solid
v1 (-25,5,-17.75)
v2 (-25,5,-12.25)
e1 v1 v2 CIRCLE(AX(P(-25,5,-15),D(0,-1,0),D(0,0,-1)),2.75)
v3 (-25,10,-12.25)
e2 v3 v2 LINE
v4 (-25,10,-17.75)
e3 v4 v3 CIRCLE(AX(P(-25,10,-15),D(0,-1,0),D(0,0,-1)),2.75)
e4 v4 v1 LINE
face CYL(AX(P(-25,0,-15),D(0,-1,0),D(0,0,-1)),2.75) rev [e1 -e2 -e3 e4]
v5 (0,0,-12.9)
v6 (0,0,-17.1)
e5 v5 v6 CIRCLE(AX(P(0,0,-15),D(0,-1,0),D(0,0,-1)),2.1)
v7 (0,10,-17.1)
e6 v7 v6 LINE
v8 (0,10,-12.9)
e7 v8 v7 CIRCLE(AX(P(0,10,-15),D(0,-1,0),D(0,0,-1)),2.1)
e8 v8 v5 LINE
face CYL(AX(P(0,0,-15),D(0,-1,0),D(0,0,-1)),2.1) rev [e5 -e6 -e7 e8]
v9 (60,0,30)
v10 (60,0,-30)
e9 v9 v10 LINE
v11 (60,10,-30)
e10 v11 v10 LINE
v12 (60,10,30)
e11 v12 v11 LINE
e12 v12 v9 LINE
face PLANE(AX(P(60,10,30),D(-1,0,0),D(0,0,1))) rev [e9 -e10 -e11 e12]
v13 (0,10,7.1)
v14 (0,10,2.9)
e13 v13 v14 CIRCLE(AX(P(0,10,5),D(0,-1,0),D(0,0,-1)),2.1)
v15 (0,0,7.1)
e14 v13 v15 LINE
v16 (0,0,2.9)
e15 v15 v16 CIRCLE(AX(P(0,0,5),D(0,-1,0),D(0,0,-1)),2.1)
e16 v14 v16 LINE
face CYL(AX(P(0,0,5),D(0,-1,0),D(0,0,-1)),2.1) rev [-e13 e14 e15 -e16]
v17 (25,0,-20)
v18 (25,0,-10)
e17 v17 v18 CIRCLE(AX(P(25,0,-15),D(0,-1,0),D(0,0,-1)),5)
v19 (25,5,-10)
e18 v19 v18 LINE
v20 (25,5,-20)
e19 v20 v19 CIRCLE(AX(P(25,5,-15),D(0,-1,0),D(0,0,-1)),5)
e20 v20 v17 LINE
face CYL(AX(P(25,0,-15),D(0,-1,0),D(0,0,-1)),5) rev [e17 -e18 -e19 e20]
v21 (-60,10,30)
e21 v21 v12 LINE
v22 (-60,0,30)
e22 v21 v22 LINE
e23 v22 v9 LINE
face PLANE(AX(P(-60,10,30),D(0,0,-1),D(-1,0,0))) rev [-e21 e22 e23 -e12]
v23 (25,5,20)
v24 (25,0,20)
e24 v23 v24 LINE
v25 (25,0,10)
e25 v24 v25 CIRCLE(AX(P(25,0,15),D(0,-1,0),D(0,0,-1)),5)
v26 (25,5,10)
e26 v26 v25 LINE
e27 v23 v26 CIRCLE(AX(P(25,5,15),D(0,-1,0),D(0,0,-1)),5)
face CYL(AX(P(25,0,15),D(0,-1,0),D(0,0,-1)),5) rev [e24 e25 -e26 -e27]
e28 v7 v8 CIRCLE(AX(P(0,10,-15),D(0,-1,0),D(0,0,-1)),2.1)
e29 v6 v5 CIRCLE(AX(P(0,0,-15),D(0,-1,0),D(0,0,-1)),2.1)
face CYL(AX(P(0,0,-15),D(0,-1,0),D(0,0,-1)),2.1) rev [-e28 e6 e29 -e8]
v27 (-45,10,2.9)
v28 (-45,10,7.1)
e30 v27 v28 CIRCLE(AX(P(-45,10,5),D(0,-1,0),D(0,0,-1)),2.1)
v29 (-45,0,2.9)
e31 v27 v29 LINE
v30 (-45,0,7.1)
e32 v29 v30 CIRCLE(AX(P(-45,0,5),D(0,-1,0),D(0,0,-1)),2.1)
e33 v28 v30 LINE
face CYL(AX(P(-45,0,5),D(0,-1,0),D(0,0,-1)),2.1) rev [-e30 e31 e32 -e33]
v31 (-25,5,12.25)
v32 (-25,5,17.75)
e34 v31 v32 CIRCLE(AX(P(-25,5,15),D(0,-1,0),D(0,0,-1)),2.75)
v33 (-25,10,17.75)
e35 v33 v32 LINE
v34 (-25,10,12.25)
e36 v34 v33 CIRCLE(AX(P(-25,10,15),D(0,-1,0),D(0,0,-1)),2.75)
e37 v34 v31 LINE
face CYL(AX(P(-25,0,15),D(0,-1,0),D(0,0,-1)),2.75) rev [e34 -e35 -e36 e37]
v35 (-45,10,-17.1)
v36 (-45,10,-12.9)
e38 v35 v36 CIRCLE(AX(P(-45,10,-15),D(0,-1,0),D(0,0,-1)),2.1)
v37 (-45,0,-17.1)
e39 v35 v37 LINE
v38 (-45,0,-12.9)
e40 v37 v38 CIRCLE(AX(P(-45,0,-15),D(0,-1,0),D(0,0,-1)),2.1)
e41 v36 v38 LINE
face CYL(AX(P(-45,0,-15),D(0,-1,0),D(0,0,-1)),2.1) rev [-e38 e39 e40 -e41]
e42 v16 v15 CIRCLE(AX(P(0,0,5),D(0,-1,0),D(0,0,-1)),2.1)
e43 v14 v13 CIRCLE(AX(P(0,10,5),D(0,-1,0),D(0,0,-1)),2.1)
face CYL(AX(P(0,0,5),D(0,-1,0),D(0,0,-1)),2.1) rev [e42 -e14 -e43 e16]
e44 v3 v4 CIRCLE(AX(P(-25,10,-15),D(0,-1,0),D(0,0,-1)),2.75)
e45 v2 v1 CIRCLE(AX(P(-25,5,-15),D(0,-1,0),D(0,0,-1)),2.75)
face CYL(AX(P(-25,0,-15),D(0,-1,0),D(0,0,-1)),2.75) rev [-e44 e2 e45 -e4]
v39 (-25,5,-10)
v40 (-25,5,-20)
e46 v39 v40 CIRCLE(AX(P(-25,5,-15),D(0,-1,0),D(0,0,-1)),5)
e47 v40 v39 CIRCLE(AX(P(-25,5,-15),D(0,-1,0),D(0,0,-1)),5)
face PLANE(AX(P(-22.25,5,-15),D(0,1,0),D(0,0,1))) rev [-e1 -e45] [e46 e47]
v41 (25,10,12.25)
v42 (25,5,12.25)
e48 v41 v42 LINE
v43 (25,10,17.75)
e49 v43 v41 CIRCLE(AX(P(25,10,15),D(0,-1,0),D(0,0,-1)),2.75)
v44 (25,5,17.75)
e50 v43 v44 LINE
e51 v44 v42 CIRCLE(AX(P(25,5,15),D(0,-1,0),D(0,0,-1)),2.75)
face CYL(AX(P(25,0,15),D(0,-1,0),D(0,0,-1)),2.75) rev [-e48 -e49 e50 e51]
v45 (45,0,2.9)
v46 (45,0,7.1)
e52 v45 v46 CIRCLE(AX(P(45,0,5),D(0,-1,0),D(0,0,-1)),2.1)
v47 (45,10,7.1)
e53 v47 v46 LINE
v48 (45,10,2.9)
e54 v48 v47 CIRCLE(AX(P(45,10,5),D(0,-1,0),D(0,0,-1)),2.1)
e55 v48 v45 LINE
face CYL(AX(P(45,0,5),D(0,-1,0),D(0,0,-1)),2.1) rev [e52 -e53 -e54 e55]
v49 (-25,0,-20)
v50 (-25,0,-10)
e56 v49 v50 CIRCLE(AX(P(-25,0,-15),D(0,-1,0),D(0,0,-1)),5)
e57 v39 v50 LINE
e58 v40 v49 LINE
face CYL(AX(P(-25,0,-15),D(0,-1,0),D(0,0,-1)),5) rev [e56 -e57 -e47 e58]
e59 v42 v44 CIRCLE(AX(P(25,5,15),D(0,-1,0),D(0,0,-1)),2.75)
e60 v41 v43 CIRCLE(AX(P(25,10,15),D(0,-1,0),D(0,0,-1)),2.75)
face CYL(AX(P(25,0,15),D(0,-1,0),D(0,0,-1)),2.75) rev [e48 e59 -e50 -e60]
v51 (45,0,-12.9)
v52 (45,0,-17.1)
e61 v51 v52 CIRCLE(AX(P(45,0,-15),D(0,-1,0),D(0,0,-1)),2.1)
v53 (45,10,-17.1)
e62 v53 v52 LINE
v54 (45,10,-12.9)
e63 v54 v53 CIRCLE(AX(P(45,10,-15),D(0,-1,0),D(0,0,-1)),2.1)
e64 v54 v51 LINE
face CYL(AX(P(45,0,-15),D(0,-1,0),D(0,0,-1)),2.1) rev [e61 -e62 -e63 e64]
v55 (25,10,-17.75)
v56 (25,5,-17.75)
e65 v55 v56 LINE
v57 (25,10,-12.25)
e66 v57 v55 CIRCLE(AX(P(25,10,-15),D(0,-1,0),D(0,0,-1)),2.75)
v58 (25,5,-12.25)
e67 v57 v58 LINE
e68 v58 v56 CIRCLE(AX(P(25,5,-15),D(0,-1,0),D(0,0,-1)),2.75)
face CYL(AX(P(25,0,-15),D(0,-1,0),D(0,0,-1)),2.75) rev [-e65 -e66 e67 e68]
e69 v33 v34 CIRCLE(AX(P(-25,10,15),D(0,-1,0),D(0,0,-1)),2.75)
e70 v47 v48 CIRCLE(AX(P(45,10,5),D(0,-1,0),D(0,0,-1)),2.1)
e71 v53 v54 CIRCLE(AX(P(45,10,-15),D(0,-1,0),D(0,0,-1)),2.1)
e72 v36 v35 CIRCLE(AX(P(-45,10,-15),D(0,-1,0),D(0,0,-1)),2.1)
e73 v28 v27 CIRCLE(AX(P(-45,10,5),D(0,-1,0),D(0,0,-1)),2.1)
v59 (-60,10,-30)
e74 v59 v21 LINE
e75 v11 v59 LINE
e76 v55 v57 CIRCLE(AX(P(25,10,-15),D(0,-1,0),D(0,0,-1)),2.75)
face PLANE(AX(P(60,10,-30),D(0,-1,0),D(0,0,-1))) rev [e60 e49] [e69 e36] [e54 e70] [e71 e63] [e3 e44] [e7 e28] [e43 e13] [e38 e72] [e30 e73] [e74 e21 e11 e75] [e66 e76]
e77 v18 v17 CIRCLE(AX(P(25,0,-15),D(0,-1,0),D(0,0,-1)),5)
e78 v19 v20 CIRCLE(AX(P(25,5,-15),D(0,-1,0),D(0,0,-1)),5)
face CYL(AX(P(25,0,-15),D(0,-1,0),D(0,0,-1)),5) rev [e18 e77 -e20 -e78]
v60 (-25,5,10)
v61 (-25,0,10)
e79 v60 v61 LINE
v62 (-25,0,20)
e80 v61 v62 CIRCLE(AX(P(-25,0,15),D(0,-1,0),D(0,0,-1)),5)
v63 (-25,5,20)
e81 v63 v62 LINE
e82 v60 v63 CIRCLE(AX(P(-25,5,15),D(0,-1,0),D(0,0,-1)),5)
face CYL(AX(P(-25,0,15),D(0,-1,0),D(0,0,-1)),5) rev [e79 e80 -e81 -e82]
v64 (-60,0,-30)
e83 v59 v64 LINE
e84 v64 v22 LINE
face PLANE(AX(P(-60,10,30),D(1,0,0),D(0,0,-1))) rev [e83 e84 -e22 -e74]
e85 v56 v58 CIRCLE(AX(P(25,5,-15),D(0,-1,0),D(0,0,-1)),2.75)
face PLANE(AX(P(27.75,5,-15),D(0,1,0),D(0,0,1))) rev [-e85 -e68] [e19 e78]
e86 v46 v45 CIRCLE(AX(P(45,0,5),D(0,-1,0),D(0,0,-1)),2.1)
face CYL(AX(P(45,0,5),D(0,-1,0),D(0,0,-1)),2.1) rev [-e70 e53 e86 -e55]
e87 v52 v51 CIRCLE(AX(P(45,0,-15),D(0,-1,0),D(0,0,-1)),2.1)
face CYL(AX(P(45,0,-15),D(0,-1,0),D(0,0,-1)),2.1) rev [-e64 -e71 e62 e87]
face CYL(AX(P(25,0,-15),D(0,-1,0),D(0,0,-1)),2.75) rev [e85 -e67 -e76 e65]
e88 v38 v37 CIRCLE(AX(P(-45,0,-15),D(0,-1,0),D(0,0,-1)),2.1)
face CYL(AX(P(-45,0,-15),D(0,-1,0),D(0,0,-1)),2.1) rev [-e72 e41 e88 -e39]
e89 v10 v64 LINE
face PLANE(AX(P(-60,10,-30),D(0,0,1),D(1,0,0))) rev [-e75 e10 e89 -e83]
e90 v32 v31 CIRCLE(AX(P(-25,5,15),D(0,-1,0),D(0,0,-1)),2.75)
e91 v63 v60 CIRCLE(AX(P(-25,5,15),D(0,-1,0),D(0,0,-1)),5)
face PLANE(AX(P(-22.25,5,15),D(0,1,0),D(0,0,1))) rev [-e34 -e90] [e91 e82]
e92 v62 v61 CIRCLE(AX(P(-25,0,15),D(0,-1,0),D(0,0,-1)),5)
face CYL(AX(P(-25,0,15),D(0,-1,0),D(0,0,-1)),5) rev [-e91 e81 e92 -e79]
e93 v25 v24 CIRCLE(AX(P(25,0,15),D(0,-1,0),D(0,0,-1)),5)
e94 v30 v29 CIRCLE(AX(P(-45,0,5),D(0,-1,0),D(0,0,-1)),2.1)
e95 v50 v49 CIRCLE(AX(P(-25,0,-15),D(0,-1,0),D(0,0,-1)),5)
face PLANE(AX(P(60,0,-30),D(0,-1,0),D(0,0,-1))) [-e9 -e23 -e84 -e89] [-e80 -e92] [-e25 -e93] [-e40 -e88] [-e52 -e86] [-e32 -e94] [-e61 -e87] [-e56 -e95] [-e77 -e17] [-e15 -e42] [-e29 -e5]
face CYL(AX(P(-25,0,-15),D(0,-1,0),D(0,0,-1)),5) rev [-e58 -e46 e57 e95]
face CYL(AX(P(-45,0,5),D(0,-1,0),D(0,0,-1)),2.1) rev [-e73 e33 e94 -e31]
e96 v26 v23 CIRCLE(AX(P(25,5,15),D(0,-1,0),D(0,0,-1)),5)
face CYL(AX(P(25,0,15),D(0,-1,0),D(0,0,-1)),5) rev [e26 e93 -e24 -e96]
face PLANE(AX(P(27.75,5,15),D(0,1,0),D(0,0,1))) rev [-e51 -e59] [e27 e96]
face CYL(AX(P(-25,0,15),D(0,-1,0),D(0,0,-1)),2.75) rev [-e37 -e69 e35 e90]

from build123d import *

# Parameters (mm, degrees)
SKETCH_1_W                                         = 120
SKETCH_1_H                                         = 60
BOSS_EXTRUDE_1_DEPTH                               = 10
M5_SOCKET_HEAD_CAP_SCREW_COUNTERBORE_1_D           = 5.5
M5_SOCKET_HEAD_CAP_SCREW_COUNTERBORE_1_CBORE_D     = 10
M5_SOCKET_HEAD_CAP_SCREW_COUNTERBORE_1_CBORE_DEPTH = 5
LINEAR_PATTERN_1_COUNT                             = 2
LINEAR_PATTERN_1_PITCH                             = 50
LINEAR_PATTERN_1_COUNT_DIR2                        = 2
LINEAR_PATTERN_1_PITCH_DIR2                        = 30
M5_TAPPED_HOLE_1_D                                 = 4.2
LINEAR_PATTERN_2_COUNT                             = 2
LINEAR_PATTERN_2_PITCH                             = 20
LINEAR_PATTERN_2_COUNT_DIR2                        = 3
LINEAR_PATTERN_2_PITCH_DIR2                        = 45


with BuildPart() as part:
    # Sketch 1 → Boss-Extrude 1 (new body)
    with BuildSketch(Plane(origin=(0, 0, 0), x_dir=(1, 0, 0), z_dir=(0, 1, 0))):
        Rectangle(SKETCH_1_W, SKETCH_1_H)
    extrude(amount=BOSS_EXTRUDE_1_DEPTH)

    # M5 Socket Head Cap Screw Counterbore 1 (through all)
    with Locations(Plane.XZ):
        with Locations((-25, 15)):
            m5_socket_head_cap_screw_counterbore_1 = CounterBoreHole(M5_SOCKET_HEAD_CAP_SCREW_COUNTERBORE_1_D / 2, M5_SOCKET_HEAD_CAP_SCREW_COUNTERBORE_1_CBORE_D / 2, M5_SOCKET_HEAD_CAP_SCREW_COUNTERBORE_1_CBORE_DEPTH)

    # Linear Pattern 1: M5 Socket Head Cap Screw Counterbore 1 2 × 2
    with Locations(*[(i * LINEAR_PATTERN_1_PITCH, 0, -j * LINEAR_PATTERN_1_PITCH_DIR2) for i in range(LINEAR_PATTERN_1_COUNT) for j in range(LINEAR_PATTERN_1_COUNT_DIR2) if (i, j) != (0, 0)]):
        add(m5_socket_head_cap_screw_counterbore_1, mode=Mode.SUBTRACT)

    # M5 Tapped Hole 1 (through all)
    with Locations(Plane.XZ):
        with Locations((-45, 5)):
            m5_tapped_hole_1 = Hole(M5_TAPPED_HOLE_1_D / 2)

    # Linear Pattern 2: M5 Tapped Hole 1 2 × 3
    with Locations(*[(j * LINEAR_PATTERN_2_PITCH_DIR2, 0, -i * LINEAR_PATTERN_2_PITCH) for i in range(LINEAR_PATTERN_2_COUNT) for j in range(LINEAR_PATTERN_2_COUNT_DIR2) if (i, j) != (0, 0)]):
        add(m5_tapped_hole_1, mode=Mode.SUBTRACT)


solid = part.part
